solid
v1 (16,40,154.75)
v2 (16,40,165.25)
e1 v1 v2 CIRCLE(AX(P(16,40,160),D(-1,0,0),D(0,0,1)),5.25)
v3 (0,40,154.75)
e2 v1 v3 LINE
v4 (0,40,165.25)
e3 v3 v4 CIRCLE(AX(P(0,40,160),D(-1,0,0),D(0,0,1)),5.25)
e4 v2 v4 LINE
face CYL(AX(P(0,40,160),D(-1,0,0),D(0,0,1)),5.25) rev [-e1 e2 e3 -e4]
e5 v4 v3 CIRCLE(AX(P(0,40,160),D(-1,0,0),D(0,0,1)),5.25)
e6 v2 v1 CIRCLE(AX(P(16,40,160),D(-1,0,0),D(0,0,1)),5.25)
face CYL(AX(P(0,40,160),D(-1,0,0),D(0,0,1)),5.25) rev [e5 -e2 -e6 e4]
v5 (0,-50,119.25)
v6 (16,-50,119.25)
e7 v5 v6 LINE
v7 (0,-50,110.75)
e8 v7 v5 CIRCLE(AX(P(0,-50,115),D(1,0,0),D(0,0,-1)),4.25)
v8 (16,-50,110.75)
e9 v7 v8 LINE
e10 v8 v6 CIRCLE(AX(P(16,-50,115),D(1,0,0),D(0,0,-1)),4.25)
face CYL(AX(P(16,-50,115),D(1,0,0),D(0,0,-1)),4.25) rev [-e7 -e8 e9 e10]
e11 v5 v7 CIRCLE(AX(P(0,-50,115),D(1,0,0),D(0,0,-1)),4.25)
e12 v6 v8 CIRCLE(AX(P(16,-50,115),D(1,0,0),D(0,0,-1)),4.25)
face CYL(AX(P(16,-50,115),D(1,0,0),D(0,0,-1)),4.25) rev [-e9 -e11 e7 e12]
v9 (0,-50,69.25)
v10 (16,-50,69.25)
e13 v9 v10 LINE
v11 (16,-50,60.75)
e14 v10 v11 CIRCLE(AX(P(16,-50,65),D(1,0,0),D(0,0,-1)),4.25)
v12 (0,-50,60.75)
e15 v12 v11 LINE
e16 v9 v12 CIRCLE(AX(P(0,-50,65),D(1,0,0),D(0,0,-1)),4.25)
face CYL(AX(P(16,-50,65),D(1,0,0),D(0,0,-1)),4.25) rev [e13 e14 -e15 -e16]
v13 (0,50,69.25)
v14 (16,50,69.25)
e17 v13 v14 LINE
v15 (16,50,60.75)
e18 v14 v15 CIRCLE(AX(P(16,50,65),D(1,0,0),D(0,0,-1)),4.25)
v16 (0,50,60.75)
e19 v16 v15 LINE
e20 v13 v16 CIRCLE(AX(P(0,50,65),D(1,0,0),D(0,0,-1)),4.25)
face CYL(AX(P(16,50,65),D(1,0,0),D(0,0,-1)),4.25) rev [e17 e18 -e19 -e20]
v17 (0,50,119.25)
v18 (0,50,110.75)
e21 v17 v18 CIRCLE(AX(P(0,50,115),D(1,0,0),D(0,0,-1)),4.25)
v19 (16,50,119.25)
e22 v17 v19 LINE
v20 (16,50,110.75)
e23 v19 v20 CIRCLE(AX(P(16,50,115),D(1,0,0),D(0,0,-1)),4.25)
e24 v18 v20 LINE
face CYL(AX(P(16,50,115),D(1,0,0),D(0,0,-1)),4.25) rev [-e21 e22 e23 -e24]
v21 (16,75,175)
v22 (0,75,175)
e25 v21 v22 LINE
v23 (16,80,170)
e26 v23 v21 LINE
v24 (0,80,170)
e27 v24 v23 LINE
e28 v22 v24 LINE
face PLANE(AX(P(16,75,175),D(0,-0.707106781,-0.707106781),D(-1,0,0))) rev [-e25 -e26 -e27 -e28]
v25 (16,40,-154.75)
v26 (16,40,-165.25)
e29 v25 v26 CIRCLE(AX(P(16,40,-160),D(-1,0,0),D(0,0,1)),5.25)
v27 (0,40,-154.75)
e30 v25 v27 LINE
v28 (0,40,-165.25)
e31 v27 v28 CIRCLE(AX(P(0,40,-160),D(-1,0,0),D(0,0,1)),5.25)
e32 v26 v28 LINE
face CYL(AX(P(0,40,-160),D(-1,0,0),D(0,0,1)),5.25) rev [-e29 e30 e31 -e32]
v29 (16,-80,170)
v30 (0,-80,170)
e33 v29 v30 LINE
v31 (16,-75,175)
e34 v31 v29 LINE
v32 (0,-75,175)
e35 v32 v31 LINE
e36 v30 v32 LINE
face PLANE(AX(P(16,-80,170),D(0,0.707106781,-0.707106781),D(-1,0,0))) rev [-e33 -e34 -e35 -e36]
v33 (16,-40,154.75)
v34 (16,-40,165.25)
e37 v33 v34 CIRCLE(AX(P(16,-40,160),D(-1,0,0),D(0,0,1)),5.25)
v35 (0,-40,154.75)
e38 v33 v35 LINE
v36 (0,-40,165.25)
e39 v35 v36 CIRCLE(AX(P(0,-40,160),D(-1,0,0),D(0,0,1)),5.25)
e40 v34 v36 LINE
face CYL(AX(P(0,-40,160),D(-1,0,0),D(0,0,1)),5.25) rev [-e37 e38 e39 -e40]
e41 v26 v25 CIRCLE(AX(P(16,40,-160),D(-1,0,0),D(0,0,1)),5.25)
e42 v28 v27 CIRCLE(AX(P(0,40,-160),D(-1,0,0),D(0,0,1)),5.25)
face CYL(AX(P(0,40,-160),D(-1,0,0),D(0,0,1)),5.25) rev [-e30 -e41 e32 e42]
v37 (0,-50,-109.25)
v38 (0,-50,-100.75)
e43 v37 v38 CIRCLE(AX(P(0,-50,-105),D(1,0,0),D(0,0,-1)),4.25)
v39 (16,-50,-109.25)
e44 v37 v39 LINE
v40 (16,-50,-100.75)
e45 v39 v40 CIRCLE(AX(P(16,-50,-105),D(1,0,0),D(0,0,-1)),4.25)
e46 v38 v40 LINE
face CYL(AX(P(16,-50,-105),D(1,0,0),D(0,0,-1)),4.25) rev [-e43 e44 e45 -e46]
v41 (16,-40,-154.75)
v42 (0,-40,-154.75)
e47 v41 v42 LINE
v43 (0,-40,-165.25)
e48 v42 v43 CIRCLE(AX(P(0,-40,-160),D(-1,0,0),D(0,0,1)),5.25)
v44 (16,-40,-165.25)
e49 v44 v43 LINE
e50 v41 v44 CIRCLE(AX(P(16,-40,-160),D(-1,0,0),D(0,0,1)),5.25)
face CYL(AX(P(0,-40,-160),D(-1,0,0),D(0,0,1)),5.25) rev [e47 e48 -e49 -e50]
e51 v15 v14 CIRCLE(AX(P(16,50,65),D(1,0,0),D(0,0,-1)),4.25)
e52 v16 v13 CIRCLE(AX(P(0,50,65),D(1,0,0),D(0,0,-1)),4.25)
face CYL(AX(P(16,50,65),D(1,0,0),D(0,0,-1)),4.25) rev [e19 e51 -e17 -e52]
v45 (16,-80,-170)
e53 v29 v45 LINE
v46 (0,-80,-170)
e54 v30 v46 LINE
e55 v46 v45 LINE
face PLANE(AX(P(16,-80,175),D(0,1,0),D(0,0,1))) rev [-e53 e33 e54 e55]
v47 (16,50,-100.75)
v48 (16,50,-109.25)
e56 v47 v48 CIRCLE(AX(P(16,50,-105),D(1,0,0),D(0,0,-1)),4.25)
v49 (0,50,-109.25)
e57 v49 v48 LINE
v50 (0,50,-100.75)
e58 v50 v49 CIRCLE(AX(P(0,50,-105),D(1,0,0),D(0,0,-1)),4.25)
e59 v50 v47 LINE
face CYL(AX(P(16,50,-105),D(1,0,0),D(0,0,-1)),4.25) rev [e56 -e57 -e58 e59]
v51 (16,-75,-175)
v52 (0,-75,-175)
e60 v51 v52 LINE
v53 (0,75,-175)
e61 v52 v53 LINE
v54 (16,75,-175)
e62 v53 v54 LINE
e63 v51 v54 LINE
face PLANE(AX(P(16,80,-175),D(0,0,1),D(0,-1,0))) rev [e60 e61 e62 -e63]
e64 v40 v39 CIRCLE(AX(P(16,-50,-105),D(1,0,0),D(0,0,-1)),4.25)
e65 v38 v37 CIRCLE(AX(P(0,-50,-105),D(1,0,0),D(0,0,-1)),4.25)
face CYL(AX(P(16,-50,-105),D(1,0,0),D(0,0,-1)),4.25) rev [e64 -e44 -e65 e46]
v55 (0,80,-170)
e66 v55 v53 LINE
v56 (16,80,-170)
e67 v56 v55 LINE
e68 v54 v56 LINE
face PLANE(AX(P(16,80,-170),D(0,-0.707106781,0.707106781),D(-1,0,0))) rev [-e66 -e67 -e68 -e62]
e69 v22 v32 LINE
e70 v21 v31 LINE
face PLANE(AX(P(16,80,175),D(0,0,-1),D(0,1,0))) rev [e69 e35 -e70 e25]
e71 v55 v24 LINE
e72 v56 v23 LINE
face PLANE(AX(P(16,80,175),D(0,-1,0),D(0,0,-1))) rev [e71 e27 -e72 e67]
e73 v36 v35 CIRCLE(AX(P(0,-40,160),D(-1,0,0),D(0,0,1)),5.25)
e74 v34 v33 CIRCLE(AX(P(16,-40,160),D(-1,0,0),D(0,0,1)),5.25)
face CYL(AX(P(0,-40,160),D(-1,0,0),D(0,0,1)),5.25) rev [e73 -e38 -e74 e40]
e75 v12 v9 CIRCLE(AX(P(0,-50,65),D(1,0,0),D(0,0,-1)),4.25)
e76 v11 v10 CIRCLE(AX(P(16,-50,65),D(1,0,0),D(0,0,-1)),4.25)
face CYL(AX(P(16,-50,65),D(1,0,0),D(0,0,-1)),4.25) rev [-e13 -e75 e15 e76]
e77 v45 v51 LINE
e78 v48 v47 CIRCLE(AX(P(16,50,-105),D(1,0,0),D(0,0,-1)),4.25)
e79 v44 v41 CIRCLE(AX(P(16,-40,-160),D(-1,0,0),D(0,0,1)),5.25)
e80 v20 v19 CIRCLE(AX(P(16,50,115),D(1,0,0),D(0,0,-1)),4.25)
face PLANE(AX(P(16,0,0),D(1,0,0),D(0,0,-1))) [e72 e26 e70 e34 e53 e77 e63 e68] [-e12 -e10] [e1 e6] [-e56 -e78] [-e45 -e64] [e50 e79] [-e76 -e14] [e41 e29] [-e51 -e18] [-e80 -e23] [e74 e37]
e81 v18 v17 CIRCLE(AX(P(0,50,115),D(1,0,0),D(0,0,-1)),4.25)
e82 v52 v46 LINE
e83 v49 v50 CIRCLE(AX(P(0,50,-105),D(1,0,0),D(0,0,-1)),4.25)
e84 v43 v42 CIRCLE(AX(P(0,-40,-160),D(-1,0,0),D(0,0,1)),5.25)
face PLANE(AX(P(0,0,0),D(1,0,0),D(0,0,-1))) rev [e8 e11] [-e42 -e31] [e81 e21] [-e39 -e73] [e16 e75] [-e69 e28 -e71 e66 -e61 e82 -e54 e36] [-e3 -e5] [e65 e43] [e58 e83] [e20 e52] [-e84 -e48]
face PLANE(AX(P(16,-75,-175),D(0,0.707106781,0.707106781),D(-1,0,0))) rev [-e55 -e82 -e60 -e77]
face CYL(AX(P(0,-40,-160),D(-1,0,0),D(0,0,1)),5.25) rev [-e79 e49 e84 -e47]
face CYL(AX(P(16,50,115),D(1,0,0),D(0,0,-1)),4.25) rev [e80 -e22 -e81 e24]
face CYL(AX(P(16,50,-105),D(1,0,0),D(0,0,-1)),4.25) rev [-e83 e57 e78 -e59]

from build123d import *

# Parameters (mm, degrees)
SKETCH_1_W                = 350
SKETCH_1_H                = 160
EXTRUDE_1_DEPTH           = 16
HOLE_WIZARD_M10_1_D       = 8.5
HOLE_WIZARD_10_5_10_5_1_D = 10.5
CHAMFER_1_SIZE            = 5


with BuildPart() as part:
    # 草图1 → 凸台-拉伸1 (new body)
    with BuildSketch(Plane(origin=(0, 0, 0), x_dir=(0, 0, -1), z_dir=(1, 0, 0))):
        Rectangle(SKETCH_1_W, SKETCH_1_H)
    extrude(amount=EXTRUDE_1_DEPTH)

    # M10 螺纹孔1 (through all)
    with Locations(Plane(origin=(16, 0, 0), x_dir=(0, 0, -1), z_dir=(1, 0, 0))):
        with Locations((-115, 50), (-115, -50), (105, 50), (105, -50), (-65, 50), (-65, -50)):
            Hole(HOLE_WIZARD_M10_1_D / 2)

    # Ø10.5 (10.5) 直径孔1 (through all)
    with Locations(Plane.ZY):
        with Locations((-160, 40), (-160, -40), (160, 40), (160, -40)):
            Hole(HOLE_WIZARD_10_5_10_5_1_D / 2)

    # 倒角1
    chamfer_1_edges = [part.edges().sort_by_distance(p)[0] for p in [
        (8, -80, -175),
        (8, -80, 175),
        (8, 80, 175),
        (8, 80, -175),
    ]]
    chamfer(chamfer_1_edges, length=CHAMFER_1_SIZE)


solid = part.part
